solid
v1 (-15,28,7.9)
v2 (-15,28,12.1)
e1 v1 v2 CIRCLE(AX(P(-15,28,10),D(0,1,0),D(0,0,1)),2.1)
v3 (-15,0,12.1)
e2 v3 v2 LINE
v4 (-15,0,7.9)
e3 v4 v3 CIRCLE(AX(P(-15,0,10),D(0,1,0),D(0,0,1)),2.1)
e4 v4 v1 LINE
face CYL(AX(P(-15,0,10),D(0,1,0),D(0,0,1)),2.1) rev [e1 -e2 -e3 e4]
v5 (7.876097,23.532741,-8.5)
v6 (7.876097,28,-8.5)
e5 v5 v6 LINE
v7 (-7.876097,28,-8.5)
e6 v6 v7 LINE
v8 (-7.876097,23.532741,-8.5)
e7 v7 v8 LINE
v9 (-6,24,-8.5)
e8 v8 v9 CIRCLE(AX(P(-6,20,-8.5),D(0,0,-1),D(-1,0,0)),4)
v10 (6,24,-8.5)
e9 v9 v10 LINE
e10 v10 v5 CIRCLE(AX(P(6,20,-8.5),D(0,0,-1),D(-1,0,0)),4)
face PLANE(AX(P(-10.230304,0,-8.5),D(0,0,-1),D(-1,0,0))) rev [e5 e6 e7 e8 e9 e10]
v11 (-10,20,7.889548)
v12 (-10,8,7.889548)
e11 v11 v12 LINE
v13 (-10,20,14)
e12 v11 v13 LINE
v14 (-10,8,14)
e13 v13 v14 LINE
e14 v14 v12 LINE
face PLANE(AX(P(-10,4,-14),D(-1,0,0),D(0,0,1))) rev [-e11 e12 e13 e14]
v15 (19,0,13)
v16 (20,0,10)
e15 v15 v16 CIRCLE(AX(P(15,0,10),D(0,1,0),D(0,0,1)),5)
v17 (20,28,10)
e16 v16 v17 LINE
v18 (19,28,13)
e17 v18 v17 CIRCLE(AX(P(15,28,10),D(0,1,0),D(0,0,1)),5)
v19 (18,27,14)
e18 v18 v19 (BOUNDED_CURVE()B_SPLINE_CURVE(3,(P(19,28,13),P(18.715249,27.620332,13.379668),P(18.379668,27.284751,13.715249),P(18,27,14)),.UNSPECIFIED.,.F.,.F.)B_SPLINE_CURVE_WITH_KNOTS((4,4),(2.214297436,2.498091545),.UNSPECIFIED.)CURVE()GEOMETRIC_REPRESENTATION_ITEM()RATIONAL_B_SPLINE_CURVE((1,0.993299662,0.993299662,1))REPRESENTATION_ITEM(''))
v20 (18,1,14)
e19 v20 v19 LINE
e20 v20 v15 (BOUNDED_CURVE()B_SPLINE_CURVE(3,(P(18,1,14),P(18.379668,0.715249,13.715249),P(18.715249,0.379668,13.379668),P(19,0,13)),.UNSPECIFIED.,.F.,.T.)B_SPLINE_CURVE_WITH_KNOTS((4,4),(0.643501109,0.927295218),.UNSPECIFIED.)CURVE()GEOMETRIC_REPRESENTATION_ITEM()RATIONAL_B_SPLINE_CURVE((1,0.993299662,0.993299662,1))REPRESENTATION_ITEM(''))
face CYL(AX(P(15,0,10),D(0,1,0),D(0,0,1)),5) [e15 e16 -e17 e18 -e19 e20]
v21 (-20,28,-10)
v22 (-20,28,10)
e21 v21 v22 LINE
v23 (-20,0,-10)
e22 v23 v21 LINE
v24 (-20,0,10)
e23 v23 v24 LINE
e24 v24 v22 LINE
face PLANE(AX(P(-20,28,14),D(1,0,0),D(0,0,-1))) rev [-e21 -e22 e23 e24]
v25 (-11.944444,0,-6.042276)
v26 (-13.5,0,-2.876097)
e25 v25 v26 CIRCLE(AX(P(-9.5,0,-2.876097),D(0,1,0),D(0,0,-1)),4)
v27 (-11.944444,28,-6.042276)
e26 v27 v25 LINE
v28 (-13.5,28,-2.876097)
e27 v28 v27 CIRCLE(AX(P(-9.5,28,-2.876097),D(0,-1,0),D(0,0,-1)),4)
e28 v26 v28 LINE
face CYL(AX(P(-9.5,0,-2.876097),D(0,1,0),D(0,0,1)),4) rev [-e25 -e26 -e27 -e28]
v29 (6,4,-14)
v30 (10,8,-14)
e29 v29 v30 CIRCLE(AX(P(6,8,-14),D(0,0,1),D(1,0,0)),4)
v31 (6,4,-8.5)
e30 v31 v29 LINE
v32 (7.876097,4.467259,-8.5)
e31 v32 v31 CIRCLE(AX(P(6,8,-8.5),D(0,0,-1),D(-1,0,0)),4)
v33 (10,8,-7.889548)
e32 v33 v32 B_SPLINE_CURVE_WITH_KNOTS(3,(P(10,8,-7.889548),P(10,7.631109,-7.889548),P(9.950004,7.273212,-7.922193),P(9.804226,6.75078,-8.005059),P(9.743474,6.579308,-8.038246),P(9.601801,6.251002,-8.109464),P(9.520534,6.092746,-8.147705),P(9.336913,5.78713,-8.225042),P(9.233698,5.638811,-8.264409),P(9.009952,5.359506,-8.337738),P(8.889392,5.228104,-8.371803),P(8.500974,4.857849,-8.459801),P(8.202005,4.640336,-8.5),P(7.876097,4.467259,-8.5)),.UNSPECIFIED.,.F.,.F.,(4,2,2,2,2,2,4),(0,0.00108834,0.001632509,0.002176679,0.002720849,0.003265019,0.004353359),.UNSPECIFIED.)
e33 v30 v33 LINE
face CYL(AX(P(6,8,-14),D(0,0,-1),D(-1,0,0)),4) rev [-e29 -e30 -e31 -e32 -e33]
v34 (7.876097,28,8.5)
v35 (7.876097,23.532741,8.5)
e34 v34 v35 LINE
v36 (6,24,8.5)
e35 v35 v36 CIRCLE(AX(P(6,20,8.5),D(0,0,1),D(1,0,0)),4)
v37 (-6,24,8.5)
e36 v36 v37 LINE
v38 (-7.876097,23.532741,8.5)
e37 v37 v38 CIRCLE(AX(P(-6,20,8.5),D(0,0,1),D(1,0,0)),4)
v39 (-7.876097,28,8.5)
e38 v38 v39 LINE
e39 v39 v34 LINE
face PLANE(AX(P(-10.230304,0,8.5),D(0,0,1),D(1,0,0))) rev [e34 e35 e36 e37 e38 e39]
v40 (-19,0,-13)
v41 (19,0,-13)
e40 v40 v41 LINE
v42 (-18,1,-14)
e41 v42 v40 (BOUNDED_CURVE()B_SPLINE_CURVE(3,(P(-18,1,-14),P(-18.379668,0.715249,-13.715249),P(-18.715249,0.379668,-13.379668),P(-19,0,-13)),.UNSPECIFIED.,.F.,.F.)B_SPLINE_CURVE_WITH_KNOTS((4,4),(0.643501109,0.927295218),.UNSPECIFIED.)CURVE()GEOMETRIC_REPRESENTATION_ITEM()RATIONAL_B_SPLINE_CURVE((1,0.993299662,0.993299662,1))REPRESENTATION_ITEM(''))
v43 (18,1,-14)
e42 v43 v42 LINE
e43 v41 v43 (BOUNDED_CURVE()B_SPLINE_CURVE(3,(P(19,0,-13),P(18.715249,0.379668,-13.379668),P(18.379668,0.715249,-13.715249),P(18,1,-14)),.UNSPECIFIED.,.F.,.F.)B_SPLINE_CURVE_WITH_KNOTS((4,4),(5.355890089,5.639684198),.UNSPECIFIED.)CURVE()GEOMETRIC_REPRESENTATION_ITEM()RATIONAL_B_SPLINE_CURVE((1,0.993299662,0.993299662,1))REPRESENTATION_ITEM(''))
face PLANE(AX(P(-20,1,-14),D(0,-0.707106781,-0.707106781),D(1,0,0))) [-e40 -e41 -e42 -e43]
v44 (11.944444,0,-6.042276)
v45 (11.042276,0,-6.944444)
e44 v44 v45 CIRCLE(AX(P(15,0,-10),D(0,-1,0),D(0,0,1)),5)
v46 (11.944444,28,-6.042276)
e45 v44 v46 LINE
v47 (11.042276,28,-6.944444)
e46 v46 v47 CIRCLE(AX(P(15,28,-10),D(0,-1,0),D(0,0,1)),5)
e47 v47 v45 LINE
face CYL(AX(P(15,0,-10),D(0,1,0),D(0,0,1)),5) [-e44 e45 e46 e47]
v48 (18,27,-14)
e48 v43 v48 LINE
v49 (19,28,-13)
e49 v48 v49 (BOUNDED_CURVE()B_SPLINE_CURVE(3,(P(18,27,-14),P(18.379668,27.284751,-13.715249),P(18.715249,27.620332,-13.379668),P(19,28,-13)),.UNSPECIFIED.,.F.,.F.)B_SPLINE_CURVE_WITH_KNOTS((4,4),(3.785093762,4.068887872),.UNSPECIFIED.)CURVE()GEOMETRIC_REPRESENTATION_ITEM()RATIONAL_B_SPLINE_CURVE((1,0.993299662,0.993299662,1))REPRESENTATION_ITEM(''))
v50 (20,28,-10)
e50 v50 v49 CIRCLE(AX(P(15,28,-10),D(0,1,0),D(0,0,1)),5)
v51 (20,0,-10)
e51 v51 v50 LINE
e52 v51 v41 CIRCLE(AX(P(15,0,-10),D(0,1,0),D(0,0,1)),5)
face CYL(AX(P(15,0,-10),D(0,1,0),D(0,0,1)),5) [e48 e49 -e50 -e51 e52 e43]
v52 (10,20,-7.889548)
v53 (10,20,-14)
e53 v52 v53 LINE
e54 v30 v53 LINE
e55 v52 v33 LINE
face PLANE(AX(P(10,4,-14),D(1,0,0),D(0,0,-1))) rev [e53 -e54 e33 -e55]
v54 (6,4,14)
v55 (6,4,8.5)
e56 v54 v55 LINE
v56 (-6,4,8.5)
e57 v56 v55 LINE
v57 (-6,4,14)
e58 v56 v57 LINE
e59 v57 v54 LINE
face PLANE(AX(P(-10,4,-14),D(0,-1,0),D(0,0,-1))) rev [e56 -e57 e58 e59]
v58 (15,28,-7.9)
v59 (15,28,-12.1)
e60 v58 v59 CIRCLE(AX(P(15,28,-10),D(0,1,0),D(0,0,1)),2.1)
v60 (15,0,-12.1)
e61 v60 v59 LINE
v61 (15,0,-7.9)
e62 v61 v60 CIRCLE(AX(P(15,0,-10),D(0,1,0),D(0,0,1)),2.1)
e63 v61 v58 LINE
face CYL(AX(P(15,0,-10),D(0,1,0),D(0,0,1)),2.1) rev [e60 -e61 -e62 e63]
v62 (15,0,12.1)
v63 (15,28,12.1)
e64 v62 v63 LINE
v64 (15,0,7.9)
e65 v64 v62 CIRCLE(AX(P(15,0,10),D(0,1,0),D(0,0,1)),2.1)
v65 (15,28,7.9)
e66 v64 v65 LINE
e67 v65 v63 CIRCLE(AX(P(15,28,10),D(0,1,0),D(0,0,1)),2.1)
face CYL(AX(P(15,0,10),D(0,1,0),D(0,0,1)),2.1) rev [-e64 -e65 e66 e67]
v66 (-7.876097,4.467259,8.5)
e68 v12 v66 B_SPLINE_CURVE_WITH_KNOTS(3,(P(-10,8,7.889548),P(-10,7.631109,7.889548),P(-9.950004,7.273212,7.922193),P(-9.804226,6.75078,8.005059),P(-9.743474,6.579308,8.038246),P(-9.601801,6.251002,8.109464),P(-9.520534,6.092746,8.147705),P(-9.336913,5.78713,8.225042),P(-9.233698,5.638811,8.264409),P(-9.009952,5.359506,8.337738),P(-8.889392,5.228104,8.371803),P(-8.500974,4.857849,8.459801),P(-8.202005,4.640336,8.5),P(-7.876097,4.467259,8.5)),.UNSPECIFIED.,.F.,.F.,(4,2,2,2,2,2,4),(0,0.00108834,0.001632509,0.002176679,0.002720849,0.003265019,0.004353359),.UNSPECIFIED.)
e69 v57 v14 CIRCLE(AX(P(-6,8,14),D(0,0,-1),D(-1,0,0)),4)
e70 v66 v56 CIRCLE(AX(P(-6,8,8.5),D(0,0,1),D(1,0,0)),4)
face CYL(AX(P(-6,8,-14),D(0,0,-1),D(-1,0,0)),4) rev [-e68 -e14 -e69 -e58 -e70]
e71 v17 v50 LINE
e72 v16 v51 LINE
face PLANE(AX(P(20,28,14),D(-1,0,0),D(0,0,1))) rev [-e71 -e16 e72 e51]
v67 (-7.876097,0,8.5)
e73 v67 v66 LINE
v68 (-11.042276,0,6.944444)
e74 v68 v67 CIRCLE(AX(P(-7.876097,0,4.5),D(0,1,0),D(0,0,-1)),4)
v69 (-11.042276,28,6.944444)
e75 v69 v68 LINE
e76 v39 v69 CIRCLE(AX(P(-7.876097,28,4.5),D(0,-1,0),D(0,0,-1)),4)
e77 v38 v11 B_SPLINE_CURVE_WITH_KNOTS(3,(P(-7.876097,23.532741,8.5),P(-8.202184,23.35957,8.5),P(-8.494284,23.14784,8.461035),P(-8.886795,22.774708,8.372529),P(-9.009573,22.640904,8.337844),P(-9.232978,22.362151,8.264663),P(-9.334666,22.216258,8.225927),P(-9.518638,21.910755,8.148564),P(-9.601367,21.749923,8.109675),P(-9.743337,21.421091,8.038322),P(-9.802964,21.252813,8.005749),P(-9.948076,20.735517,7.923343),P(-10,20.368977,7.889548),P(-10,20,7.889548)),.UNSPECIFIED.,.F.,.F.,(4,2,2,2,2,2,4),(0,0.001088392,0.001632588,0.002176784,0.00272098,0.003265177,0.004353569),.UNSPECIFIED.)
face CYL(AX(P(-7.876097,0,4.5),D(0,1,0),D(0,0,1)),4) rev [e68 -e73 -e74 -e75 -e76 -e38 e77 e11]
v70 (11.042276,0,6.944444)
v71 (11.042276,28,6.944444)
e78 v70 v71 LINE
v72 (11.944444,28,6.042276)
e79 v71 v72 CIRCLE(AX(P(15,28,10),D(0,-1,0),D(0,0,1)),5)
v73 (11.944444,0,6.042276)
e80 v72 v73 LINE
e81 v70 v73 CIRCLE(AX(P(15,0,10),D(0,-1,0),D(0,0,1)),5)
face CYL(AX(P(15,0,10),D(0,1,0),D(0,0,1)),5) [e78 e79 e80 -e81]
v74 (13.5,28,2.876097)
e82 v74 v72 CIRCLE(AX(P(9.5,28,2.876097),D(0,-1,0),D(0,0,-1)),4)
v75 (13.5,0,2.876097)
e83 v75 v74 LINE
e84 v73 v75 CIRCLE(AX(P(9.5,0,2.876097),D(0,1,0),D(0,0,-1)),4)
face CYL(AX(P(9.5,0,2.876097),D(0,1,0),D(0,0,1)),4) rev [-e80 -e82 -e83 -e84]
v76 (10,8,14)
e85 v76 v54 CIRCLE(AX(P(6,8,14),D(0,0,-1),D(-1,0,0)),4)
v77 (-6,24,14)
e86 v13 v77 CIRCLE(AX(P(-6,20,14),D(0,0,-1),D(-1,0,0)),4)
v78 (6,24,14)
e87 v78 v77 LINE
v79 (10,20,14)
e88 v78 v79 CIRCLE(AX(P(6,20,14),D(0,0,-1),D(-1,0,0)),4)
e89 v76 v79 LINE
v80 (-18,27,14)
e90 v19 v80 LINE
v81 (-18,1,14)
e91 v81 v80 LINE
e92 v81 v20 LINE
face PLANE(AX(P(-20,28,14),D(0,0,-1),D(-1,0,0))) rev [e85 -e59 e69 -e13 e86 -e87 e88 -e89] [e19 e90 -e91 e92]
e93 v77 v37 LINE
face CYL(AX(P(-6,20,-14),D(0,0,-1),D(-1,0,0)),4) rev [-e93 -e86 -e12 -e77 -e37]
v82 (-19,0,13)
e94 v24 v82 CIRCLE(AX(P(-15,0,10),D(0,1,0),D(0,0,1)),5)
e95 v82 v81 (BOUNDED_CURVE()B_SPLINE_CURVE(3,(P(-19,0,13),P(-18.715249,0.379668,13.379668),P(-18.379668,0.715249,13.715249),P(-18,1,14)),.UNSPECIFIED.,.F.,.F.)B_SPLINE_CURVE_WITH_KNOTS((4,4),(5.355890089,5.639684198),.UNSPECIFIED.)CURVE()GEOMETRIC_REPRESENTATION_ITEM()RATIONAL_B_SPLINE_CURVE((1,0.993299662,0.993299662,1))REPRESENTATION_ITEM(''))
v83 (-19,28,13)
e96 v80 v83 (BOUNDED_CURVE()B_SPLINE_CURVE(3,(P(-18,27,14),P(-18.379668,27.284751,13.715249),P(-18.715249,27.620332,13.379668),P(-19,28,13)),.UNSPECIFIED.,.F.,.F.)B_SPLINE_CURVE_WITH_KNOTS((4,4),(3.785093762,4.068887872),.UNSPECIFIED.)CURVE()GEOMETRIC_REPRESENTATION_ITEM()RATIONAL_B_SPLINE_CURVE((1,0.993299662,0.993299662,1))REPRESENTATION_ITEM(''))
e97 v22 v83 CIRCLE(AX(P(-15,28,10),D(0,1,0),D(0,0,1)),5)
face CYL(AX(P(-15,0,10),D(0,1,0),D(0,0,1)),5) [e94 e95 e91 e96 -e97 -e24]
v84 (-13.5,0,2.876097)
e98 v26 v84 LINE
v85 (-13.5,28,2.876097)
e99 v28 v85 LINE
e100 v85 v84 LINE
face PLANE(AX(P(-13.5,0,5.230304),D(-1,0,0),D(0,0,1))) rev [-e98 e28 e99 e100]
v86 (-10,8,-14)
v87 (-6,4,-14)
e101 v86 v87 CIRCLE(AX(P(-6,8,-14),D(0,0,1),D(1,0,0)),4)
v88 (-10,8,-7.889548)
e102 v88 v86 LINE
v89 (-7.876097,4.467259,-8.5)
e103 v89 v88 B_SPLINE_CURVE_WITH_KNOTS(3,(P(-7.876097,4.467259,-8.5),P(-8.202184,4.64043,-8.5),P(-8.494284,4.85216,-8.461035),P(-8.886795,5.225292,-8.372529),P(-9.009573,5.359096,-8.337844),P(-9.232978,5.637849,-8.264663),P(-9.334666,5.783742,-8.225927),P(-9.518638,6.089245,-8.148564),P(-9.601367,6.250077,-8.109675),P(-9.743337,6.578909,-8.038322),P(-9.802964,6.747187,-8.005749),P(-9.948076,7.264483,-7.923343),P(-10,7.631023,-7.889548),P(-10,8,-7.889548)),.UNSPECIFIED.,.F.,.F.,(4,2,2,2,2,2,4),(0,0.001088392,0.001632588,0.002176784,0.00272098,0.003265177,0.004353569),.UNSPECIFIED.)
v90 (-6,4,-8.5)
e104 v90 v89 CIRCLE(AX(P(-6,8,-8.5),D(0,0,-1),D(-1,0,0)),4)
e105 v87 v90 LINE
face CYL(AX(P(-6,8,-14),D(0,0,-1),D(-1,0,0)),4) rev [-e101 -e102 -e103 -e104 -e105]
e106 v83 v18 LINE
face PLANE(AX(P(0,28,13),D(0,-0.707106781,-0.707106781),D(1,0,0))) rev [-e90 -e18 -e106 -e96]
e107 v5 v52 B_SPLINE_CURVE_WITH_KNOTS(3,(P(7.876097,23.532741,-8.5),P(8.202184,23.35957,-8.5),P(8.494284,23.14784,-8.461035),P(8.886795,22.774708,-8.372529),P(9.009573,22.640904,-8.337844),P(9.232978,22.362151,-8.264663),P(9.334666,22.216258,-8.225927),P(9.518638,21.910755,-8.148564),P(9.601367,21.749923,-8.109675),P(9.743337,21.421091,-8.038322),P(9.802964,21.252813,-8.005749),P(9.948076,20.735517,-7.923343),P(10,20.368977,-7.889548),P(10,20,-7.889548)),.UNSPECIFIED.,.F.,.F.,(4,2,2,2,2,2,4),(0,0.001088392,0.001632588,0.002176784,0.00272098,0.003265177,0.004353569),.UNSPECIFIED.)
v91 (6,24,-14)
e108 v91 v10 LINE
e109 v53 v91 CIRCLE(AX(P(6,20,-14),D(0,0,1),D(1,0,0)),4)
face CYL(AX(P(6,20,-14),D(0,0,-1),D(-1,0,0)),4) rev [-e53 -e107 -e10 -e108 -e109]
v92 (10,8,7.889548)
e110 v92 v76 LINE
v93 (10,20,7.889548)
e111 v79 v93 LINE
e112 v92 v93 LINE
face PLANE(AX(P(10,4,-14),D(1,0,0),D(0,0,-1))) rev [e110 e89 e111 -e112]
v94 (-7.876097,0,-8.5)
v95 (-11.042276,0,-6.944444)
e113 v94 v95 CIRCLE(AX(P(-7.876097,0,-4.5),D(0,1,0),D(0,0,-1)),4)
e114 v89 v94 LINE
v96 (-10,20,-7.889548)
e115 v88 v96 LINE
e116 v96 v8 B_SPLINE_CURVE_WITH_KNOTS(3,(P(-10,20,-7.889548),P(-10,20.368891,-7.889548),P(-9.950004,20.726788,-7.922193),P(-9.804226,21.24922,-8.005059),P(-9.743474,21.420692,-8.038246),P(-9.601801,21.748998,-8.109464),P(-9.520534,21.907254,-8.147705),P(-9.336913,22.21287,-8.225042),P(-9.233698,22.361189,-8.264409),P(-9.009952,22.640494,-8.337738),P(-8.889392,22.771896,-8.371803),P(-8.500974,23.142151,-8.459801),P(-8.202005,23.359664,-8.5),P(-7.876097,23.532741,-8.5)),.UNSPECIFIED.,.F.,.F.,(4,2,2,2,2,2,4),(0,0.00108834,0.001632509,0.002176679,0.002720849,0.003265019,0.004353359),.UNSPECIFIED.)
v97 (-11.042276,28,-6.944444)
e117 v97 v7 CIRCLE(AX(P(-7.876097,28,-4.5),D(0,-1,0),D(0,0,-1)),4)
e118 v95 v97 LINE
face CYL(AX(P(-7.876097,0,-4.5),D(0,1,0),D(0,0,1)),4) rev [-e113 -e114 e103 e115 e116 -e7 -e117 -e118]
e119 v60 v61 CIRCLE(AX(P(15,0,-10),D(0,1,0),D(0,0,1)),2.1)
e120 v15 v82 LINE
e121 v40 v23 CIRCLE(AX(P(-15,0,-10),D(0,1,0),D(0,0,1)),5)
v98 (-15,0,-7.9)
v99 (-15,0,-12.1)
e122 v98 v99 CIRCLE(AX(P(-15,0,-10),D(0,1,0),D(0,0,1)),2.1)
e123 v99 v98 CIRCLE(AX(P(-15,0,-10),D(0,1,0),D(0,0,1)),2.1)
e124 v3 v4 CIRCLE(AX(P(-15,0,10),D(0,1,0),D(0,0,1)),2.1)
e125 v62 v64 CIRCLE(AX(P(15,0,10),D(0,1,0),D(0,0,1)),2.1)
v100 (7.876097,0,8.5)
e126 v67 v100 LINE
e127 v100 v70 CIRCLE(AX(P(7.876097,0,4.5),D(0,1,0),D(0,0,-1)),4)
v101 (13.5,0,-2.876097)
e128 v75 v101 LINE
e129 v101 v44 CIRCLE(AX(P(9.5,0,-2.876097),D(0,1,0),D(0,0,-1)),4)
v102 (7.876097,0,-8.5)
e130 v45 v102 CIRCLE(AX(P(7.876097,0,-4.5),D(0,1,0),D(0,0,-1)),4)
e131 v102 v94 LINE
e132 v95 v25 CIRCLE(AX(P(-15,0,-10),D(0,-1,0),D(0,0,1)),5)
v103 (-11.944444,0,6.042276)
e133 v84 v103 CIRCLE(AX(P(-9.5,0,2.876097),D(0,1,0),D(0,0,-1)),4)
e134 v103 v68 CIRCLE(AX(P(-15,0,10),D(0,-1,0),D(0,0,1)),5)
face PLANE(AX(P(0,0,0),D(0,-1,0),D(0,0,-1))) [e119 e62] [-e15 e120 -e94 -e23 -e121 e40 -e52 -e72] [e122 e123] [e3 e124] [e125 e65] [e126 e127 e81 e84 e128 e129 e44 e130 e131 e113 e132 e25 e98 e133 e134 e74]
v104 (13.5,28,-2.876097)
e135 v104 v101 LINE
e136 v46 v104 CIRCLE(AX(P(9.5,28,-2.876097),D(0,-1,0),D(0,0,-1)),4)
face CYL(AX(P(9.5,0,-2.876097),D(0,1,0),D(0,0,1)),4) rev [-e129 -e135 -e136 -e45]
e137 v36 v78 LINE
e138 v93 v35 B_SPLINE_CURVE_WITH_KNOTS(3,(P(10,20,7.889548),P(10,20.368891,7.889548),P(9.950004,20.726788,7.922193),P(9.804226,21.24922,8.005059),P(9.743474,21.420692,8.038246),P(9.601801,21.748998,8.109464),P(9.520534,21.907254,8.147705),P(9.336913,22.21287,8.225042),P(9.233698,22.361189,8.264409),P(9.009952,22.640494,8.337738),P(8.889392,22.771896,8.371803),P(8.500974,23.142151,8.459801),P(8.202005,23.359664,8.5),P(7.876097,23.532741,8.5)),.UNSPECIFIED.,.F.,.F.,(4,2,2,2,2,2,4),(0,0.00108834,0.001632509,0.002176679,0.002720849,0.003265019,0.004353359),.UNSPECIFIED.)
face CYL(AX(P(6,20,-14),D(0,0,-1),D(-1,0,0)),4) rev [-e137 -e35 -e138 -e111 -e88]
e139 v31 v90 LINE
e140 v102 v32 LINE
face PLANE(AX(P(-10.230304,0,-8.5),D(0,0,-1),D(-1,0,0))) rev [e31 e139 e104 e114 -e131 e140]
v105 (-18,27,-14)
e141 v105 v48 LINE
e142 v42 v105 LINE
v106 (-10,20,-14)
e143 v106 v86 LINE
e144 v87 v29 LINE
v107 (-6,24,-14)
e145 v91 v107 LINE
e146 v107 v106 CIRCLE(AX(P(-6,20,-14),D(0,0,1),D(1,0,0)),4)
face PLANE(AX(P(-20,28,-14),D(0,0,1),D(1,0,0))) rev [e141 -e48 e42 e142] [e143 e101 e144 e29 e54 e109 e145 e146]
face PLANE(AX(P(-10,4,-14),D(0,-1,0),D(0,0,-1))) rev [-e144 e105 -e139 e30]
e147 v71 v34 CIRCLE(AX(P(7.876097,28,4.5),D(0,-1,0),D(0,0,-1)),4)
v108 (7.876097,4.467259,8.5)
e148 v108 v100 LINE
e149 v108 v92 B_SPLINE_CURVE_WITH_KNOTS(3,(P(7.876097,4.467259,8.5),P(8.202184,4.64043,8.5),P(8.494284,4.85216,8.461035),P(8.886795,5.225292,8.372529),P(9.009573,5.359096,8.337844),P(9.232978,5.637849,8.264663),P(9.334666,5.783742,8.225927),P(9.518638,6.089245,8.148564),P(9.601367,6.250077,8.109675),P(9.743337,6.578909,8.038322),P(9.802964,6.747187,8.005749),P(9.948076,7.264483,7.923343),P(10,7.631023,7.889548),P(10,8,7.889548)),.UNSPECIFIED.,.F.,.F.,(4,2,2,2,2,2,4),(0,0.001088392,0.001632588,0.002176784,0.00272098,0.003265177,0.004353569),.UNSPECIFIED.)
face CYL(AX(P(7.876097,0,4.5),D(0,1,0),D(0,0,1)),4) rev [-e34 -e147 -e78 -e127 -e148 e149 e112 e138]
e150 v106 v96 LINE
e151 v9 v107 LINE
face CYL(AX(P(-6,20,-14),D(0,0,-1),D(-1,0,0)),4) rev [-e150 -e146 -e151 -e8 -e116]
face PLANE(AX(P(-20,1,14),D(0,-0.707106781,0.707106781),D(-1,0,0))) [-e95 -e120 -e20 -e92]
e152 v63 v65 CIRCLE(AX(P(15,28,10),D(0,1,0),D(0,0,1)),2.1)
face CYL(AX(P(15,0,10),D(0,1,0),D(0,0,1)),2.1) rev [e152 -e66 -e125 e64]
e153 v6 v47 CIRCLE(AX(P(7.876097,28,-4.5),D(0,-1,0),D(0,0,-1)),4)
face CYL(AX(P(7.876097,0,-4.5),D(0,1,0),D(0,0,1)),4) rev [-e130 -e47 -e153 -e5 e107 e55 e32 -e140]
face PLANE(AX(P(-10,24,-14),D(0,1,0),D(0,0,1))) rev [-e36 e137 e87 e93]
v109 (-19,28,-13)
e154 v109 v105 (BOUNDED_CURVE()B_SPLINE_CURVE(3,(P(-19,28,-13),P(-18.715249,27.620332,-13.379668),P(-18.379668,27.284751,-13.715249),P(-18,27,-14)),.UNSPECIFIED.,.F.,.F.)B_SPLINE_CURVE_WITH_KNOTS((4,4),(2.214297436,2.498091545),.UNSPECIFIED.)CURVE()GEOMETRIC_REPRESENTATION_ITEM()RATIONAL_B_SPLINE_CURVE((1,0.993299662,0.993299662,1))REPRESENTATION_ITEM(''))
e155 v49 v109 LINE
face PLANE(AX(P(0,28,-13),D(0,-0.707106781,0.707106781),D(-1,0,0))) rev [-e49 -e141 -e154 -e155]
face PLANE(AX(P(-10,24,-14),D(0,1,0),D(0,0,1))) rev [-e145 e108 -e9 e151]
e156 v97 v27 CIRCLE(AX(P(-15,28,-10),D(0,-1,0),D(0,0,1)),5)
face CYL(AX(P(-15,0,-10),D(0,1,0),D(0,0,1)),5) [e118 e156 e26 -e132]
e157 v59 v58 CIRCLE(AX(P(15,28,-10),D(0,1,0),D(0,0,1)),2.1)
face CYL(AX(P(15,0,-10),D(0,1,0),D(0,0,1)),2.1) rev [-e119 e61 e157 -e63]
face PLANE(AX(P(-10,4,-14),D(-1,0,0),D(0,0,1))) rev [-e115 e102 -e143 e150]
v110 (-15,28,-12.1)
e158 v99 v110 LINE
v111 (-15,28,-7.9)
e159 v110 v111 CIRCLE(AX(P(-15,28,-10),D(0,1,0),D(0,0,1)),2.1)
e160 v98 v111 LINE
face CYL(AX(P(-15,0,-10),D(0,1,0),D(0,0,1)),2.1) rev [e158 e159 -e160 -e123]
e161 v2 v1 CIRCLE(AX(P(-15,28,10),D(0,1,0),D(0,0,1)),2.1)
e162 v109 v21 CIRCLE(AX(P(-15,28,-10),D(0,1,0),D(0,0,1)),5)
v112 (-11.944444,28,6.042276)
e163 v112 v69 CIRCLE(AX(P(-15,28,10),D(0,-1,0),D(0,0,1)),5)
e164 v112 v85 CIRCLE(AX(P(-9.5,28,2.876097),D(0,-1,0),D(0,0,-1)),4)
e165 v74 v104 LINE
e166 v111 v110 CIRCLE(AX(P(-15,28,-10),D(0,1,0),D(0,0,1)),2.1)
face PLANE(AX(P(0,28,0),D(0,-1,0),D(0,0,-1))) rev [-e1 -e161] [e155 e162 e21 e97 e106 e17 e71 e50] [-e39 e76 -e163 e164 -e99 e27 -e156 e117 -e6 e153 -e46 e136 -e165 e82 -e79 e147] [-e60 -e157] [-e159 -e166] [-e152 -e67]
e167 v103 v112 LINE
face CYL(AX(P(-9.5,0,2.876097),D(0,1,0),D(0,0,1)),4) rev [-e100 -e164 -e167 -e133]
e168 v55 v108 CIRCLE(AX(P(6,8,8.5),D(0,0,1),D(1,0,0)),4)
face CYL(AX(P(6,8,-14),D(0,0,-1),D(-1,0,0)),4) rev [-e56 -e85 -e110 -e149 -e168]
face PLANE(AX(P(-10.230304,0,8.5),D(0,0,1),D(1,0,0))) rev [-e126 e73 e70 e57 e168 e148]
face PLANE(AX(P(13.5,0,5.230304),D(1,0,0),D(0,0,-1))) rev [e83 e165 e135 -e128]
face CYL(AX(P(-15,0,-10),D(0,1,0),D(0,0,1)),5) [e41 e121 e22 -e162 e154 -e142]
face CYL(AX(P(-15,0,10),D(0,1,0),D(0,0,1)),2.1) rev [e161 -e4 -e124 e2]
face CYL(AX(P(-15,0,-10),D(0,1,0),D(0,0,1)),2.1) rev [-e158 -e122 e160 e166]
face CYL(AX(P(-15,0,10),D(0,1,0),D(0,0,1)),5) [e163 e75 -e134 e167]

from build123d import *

# Parameters (mm, degrees)
SKETCH_1_W          = 40
SKETCH_1_H          = 28
EXTRUDE_1_DEPTH     = 28
SKETCH_2_R          = 2.1
CUT_EXTRUDE_1_DEPTH = 38.148351242
SKETCH_3_OUTSIDE_W  = 53.256
SKETCH_3_OUTSIDE_H  = 41.256
CUT_EXTRUDE_2_DEPTH = 38.148351242
FILLET_3_R          = 4
SKETCH_6_W          = 20
SKETCH_6_H          = 20
CUT_EXTRUDE_4_DEPTH = 45.362146026
FILLET_4_R          = 4
CHAMFER_1_SIZE      = 1


with BuildPart() as part:
    # 草图1 → 凸台-拉伸1 (new body)
    with BuildSketch(Plane(origin=(0, 0, 0), x_dir=(1, 0, 0), z_dir=(0, 1, 0))):
        Rectangle(SKETCH_1_W, SKETCH_1_H)
    extrude(amount=EXTRUDE_1_DEPTH)

    # 草图2 → 切除-拉伸1 (cut, through all)
    with BuildSketch(Plane(origin=(0, 28, 0), x_dir=(1, 0, 0), z_dir=(0, 1, 0))):
        with Locations(Location((-15, 10, 0), (0, 0, 270))):
            Circle(SKETCH_2_R)
        with Locations(Location((-15, -10, 0), (0, 0, 270))):
            Circle(SKETCH_2_R)
        with Locations(Location((15, -10, 0), (0, 0, 270))):
            Circle(SKETCH_2_R)
        with Locations(Location((15, 10, 0), (0, 0, 270))):
            Circle(SKETCH_2_R)
    extrude(amount=-CUT_EXTRUDE_1_DEPTH, mode=Mode.SUBTRACT)

    # 草图3 outside → 切除-拉伸2 (cut, through all)
    # profile 1 of 2: a face of its own
    with BuildSketch(Plane(origin=(0, 28, 0), x_dir=(1, 0, 0), z_dir=(0, 1, 0))):
        Rectangle(SKETCH_3_OUTSIDE_W, SKETCH_3_OUTSIDE_H)
        with BuildLine():
            Line((20, -10), (20, 10))
            ThreePointArc((20, 10), (17.236067977, 14.472135955), (12, 14))
            Line((12, 14), (-18, 14))
            ThreePointArc((-18, 14), (-19.472135955, 12.236067977), (-20, 10))
            Line((-20, 10), (-20, -10))
            ThreePointArc((-20, -10), (-17.236067977, -14.472135955), (-12, -14))
            Line((-12, -14), (18, -14))
            ThreePointArc((18, -14), (19.472135955, -12.236067977), (20, -10))
        make_face(mode=Mode.SUBTRACT)
    # profile 2 of 2: a face of its own
    with BuildSketch(Plane(origin=(0, 28, 0), x_dir=(1, 0, 0), z_dir=(0, 1, 0))):
        with BuildLine():
            Line((-13.5, -5.230303993), (-13.5, 5.230303993))
            ThreePointArc((-13.5, 5.230303993), (-11.464466094, 6.464466094), (-10.230303993, 8.5))
            Line((-10.230303993, 8.5), (10.230303993, 8.5))
            ThreePointArc((10.230303993, 8.5), (11.464466094, 6.464466094), (13.5, 5.230303993))
            Line((13.5, 5.230303993), (13.5, -5.230303993))
            ThreePointArc((13.5, -5.230303993), (11.464466094, -6.464466094), (10.230303993, -8.5))
            Line((10.230303993, -8.5), (-10.230303993, -8.5))
            ThreePointArc((-10.230303993, -8.5), (-11.464466094, -6.464466094), (-13.5, -5.230303993))
        make_face()
    extrude(amount=-CUT_EXTRUDE_2_DEPTH, mode=Mode.SUBTRACT)

    # 圆角3
    fillet_3_edges = [part.edges().sort_by_distance(p)[0] for p in [
        (-13.5, 14, -5.230303993),
        (-10.230303993, 14, -8.5),
        (10.230303993, 14, -8.5),
        (13.5, 14, -5.230303993),
        (13.5, 14, 5.230303993),
        (10.230303993, 14, 8.5),
        (-10.230303993, 14, 8.5),
        (-13.5, 14, 5.230303993),
    ]]
    fillet(fillet_3_edges, radius=FILLET_3_R)

    # 草图6 → 切除-拉伸4 (cut, through all)
    with BuildSketch(Plane.XY.offset(14)):
        with Locations((0, 14)):
            Rectangle(SKETCH_6_W, SKETCH_6_H)
    extrude(amount=-CUT_EXTRUDE_4_DEPTH, mode=Mode.SUBTRACT)

    # 圆角4
    fillet_4_edges = [part.edges().sort_by_distance(p)[0] for p in [
        (10, 4, -10.944773897),
        (-10, 4, -10.944773897),
        (-10, 24, -10.944773897),
        (10, 24, -10.944773897),
        (10, 4, 10.944773897),
        (-10, 4, 10.944773897),
        (-10, 24, 10.944773897),
        (10, 24, 10.944773897),
    ]]
    fillet(fillet_4_edges, radius=FILLET_4_R)

    # 倒角1
    chamfer_1_edges = [part.edges().sort_by_distance(p)[0] for p in [
        (0, 0, 14),
        (0, 0, -14),
        (0, 28, -14),
        (0, 28, 14),
    ]]
    chamfer(chamfer_1_edges, length=CHAMFER_1_SIZE)


solid = part.part
